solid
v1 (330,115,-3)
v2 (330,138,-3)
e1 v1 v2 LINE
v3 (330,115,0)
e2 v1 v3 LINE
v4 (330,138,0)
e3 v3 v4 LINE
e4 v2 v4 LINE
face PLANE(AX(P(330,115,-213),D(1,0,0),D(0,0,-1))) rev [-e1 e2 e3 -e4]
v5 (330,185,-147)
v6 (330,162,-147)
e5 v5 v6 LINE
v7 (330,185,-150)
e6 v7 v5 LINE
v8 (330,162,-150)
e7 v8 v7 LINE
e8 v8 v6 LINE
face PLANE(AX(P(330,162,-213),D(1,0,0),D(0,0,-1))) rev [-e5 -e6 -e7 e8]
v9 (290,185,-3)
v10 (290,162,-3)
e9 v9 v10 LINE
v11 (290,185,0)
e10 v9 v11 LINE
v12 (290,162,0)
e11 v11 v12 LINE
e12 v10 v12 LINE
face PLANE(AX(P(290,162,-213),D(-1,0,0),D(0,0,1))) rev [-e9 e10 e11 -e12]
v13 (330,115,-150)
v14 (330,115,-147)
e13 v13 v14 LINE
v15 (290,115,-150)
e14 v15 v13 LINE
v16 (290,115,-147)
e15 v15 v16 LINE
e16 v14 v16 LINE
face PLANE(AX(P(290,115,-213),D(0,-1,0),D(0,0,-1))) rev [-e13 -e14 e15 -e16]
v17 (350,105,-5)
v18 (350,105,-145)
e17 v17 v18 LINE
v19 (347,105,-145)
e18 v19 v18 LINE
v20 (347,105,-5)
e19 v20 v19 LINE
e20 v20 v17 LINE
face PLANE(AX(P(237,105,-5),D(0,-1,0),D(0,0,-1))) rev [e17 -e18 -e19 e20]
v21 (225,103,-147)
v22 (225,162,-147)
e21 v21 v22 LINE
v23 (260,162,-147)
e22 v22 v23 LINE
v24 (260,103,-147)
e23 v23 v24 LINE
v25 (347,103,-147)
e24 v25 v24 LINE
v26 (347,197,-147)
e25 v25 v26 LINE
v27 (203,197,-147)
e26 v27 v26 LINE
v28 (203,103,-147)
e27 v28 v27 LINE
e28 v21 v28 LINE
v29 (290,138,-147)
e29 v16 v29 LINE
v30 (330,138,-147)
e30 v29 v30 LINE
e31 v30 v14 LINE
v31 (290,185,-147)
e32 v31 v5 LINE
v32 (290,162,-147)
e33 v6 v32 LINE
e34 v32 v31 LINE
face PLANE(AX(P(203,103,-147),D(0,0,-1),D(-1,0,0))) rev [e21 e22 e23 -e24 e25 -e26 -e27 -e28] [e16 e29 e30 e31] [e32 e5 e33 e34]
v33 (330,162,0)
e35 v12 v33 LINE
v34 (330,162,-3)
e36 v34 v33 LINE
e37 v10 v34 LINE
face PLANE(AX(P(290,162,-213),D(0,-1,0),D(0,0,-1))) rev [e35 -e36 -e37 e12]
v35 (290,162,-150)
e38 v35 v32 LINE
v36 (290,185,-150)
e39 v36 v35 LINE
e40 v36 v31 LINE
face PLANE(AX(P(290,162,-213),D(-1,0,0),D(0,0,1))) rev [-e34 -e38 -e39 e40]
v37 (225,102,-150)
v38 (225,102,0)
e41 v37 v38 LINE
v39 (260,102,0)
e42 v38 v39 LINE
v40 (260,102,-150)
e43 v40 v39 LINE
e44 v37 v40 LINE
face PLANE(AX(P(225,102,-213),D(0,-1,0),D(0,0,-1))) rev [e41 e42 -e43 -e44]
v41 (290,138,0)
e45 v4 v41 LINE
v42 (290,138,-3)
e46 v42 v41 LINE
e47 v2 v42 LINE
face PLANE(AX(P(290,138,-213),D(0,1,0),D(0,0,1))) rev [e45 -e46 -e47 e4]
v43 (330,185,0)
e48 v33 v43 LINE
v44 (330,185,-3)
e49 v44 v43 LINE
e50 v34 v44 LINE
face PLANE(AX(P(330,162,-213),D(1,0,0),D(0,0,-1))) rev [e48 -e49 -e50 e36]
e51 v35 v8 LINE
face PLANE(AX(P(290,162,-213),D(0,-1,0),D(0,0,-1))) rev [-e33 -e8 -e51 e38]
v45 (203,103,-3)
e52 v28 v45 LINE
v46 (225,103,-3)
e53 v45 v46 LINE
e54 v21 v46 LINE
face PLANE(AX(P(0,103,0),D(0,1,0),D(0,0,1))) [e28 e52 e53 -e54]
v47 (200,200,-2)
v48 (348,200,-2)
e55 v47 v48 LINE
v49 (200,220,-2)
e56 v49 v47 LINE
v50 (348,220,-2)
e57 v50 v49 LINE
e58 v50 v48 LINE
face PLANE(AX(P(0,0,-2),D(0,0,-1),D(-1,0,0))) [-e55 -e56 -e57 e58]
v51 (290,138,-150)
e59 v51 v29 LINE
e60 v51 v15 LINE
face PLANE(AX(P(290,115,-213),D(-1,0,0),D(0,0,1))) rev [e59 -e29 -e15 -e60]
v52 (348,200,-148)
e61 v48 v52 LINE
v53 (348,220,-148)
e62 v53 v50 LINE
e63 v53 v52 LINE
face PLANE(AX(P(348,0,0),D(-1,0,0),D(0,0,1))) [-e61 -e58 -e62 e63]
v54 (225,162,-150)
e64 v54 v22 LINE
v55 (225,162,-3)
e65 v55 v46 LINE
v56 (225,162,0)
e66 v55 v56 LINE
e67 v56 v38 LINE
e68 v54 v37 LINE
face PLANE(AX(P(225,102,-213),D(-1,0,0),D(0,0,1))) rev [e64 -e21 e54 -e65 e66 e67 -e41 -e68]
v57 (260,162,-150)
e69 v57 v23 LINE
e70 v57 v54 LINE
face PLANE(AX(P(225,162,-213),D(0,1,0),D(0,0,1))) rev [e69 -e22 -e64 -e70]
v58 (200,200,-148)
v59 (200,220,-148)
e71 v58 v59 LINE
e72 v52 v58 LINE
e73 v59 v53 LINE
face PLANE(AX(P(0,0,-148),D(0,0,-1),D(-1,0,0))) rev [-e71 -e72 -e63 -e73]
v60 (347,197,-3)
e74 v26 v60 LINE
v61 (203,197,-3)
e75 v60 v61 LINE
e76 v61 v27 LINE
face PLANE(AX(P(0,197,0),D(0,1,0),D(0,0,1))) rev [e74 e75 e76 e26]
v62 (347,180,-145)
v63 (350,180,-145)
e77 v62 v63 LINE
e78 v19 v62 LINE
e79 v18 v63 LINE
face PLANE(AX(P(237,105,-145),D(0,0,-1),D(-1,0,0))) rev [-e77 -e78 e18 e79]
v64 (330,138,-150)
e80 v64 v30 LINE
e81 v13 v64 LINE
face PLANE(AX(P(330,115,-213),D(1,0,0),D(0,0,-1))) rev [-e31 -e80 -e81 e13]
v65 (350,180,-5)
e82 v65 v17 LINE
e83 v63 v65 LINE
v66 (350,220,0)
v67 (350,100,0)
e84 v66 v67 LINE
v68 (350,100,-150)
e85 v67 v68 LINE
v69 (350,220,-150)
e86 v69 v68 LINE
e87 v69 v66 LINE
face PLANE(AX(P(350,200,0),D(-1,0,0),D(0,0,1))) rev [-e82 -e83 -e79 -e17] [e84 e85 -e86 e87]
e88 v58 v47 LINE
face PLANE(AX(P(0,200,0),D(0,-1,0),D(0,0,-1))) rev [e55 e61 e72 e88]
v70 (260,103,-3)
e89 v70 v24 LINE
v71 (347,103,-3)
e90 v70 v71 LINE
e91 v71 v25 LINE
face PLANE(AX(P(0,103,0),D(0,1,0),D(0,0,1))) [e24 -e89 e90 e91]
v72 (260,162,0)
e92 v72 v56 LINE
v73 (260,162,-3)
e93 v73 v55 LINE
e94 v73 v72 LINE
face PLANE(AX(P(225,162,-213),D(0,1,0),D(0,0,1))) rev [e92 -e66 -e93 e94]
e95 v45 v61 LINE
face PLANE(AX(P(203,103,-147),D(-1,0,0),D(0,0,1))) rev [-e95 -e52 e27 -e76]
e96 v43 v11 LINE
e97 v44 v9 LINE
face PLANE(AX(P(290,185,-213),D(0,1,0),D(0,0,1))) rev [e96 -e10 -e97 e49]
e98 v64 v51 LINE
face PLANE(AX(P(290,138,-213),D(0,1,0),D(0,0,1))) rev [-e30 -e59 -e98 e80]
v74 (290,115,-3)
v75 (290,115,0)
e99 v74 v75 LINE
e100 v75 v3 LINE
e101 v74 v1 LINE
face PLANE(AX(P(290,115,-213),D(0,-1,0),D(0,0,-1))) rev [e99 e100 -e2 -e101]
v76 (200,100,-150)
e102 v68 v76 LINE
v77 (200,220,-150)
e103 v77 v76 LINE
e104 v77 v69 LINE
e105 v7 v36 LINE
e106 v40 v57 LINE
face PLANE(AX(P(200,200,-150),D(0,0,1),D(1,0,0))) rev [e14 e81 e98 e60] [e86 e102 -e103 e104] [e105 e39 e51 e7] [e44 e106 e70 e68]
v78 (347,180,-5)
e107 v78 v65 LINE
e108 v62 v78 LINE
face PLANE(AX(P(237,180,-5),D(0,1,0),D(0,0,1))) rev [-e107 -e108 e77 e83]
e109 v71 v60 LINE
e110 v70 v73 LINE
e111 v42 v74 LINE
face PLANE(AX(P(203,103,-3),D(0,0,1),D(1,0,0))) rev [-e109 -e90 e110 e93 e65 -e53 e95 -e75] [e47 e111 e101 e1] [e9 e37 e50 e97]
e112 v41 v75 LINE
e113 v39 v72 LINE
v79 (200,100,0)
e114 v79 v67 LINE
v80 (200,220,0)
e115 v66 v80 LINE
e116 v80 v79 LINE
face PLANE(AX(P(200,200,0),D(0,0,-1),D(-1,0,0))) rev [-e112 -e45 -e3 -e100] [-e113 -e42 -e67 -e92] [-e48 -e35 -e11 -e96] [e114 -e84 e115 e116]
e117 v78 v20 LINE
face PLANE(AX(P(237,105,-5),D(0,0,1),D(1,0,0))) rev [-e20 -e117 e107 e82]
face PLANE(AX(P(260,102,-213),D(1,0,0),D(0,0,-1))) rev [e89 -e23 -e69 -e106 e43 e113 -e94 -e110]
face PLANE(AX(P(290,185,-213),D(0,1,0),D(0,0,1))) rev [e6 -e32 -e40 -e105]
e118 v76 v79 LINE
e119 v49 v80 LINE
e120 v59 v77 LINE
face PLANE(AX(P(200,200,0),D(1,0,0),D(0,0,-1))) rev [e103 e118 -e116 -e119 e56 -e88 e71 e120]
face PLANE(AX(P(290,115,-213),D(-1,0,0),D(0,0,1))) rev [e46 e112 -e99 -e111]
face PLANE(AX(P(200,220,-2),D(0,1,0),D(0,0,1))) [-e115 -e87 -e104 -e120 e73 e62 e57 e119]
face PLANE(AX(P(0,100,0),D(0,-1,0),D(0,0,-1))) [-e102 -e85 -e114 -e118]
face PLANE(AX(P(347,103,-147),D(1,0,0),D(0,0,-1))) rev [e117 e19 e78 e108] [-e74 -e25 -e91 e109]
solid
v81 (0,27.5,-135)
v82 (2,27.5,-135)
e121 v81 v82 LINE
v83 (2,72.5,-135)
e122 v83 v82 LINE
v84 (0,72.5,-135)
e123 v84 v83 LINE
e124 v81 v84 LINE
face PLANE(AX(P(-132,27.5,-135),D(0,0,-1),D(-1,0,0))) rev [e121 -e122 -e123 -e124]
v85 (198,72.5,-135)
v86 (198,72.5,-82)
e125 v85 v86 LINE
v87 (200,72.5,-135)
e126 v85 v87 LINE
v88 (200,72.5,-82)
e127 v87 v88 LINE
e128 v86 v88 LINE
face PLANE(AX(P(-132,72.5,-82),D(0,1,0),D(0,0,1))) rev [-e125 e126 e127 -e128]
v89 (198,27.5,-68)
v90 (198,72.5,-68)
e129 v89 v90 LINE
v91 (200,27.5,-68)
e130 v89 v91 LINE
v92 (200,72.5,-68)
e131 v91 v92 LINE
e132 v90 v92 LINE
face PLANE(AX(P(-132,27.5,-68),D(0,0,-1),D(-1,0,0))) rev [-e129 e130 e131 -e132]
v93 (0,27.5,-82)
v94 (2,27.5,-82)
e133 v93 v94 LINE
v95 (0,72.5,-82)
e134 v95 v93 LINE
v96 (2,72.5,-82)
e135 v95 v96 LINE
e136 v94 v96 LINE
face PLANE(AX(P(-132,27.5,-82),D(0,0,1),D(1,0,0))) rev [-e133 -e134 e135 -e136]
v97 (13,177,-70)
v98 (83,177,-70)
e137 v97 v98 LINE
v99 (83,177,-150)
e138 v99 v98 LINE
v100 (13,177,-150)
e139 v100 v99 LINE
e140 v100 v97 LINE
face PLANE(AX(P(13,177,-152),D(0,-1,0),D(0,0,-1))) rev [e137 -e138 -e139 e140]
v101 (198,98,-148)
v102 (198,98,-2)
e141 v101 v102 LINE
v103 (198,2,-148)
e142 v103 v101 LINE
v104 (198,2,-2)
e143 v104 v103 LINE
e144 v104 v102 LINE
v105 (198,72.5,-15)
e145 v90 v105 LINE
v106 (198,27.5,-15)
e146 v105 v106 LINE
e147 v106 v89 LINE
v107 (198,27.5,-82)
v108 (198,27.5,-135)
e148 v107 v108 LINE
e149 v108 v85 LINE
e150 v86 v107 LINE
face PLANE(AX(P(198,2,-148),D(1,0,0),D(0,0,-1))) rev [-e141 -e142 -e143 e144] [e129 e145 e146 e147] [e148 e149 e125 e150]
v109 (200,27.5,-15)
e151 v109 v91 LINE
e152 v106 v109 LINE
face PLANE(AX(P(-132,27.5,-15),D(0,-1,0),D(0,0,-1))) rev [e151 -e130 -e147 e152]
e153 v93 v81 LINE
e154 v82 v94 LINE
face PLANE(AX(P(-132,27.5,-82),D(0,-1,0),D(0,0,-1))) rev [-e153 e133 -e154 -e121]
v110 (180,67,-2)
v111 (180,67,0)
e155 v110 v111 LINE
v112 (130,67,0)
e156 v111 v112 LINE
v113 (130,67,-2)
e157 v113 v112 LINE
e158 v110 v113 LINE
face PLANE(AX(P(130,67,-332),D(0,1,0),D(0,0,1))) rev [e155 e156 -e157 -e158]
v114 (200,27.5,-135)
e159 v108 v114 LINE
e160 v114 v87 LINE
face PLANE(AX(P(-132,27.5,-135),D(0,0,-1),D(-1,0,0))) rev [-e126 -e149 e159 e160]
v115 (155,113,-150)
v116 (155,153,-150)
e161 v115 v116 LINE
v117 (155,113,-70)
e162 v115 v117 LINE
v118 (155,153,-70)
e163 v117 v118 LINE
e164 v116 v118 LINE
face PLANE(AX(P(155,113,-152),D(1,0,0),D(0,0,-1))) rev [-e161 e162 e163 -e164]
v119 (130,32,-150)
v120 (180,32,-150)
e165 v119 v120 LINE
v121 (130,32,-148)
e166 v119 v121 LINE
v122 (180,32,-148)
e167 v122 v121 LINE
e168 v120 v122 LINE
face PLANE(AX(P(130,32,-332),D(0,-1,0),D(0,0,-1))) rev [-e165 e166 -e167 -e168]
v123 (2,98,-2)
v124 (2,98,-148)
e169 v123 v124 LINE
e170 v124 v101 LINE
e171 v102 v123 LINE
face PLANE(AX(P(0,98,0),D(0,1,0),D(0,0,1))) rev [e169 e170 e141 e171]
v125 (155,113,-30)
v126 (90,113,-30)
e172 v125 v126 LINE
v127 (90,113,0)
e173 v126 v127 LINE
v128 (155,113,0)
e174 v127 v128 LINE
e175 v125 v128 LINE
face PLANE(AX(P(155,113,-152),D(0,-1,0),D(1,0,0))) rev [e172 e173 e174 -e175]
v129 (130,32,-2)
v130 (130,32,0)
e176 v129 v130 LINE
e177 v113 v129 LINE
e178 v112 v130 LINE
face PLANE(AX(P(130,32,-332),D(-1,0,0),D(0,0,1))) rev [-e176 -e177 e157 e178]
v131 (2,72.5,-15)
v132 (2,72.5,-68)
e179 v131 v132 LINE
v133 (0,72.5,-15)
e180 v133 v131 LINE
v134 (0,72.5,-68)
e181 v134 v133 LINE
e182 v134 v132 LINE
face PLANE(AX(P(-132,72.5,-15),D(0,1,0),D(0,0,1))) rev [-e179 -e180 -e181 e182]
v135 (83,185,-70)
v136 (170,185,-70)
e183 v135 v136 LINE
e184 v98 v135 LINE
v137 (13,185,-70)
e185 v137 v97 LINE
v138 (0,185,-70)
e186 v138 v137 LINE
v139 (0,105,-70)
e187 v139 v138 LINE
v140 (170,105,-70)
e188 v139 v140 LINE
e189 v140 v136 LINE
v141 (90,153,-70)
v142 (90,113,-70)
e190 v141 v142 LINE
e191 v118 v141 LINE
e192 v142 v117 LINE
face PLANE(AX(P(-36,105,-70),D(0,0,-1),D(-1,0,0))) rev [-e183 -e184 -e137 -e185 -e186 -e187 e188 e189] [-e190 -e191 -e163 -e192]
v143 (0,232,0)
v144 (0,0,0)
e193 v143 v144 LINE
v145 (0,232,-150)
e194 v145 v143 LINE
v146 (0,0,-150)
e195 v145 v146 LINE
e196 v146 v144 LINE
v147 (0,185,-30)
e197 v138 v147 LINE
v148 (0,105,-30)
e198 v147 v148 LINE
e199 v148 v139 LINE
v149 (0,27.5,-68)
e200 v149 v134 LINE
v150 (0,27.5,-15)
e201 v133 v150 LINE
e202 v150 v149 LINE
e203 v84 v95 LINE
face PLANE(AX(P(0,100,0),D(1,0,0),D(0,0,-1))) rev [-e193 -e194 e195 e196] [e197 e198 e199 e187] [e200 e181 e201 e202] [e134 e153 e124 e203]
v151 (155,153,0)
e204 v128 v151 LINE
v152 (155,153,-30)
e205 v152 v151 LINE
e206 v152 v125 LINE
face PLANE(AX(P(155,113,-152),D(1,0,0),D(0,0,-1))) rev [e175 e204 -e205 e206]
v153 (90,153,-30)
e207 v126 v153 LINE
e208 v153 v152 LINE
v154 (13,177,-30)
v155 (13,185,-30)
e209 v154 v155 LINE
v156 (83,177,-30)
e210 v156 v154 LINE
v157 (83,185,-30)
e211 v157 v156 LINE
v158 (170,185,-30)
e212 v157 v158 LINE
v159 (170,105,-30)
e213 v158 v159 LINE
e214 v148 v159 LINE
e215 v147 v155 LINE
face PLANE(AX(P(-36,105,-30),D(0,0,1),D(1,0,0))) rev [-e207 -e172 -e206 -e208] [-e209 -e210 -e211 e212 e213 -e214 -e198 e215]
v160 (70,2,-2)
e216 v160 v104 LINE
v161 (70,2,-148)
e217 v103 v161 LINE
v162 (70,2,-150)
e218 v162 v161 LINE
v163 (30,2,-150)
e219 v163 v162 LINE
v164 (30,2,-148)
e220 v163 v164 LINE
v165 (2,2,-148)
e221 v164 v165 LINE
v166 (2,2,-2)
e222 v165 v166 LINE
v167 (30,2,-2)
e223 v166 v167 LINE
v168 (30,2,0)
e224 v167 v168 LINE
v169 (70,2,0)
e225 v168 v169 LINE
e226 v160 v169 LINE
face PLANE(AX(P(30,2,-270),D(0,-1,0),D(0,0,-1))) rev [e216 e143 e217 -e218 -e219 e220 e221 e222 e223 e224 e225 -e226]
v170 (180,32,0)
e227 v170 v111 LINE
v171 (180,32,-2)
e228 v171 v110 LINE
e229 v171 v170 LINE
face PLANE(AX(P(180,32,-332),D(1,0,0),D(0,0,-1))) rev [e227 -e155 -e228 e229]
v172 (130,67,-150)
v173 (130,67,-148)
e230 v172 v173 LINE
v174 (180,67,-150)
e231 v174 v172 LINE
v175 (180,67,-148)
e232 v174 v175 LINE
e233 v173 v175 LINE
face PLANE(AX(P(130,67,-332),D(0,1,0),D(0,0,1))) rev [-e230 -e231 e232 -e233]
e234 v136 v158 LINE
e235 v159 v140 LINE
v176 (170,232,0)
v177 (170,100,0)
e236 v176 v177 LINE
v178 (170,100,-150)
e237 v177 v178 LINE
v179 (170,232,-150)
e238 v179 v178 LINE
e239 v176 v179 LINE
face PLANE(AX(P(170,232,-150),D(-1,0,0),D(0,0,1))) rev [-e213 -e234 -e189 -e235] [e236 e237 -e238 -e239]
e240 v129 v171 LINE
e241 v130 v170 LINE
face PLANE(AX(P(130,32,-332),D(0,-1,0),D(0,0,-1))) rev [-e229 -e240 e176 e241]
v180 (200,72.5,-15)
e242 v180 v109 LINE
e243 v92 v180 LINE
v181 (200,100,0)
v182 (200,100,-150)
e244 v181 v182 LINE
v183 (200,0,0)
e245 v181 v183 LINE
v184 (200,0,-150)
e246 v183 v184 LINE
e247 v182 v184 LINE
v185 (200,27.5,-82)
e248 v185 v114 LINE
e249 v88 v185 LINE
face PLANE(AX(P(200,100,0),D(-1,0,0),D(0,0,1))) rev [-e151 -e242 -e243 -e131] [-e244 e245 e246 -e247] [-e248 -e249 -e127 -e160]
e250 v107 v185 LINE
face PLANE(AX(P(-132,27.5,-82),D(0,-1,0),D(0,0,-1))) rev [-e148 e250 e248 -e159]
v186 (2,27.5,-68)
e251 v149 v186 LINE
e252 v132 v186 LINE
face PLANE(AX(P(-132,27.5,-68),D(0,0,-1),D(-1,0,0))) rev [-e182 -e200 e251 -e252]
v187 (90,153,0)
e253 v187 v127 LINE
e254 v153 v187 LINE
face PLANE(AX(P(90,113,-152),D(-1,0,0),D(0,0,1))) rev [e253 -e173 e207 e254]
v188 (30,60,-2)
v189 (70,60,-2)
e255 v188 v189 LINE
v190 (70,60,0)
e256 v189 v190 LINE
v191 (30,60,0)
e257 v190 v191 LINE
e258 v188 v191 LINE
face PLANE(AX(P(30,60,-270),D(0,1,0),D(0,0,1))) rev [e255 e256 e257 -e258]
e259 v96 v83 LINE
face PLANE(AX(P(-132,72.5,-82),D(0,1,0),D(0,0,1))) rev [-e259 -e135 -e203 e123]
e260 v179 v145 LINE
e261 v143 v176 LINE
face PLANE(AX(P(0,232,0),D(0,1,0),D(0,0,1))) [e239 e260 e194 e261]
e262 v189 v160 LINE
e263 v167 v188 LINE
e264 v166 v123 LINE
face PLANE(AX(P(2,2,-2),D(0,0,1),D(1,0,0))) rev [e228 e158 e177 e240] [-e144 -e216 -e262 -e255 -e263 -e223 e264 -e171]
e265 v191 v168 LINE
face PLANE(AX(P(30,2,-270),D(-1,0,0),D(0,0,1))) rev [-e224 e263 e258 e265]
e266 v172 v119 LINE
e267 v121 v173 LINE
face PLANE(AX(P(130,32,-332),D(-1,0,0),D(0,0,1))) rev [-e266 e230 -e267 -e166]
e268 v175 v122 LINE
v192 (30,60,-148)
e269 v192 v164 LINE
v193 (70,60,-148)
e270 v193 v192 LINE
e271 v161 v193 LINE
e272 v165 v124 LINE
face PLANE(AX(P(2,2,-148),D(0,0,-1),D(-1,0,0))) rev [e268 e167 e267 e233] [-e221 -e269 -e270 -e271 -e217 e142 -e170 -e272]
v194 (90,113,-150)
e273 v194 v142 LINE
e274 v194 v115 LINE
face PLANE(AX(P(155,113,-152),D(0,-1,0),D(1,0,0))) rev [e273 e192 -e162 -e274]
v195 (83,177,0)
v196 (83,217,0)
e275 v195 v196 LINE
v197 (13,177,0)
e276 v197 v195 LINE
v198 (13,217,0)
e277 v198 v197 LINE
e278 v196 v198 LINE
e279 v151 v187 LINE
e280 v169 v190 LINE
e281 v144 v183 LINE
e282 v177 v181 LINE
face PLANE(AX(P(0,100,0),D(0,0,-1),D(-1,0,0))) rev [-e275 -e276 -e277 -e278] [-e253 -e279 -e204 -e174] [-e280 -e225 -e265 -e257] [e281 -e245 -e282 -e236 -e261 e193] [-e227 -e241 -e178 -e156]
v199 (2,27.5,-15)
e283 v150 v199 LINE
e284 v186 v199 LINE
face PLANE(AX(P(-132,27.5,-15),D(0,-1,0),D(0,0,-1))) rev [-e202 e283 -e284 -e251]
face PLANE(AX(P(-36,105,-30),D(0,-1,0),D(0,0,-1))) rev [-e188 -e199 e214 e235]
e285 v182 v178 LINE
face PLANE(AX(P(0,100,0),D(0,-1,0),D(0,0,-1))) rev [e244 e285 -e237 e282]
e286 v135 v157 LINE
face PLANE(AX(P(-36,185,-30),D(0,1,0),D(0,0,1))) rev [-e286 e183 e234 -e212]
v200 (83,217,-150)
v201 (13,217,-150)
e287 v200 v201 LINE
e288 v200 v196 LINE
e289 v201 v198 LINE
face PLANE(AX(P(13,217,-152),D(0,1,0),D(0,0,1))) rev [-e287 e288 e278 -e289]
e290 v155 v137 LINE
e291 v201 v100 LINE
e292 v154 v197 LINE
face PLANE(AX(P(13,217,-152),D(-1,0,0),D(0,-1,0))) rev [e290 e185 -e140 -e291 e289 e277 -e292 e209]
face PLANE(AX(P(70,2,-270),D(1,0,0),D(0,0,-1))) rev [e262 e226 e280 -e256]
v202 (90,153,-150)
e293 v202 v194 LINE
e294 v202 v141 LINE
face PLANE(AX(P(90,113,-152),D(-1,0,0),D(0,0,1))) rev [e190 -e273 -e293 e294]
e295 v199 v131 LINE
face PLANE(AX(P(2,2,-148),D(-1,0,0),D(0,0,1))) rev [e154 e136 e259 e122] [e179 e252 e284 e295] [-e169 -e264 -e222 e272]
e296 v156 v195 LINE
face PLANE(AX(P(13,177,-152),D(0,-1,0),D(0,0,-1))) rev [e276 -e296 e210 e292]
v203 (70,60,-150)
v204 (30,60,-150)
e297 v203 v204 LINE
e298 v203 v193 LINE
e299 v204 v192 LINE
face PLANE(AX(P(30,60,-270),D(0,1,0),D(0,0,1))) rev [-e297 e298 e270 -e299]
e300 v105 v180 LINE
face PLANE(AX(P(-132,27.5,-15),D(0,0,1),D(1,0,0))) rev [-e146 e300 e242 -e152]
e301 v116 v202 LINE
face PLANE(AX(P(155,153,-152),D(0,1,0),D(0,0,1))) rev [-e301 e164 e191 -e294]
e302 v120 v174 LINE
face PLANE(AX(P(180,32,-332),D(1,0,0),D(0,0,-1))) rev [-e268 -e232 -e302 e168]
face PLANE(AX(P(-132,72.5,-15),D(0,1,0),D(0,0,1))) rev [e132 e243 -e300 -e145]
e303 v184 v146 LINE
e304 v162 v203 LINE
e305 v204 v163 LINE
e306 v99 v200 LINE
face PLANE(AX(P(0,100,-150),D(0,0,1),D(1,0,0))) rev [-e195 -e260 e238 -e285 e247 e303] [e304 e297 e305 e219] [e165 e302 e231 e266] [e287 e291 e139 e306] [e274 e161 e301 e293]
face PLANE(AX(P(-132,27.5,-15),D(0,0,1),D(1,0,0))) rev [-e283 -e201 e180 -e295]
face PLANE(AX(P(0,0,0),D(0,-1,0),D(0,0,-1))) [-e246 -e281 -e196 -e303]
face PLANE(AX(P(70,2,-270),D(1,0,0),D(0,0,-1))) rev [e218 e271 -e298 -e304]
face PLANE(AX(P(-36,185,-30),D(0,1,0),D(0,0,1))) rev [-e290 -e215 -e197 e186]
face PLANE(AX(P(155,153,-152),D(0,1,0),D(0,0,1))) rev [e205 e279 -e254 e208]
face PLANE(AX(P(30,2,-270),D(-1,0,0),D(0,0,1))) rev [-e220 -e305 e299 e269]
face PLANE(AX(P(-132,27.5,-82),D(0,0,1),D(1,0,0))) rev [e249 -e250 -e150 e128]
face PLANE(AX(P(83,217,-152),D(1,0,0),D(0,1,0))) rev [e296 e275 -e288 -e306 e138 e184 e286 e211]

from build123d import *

# Parameters (mm, degrees)
BASE_BLOCK_SKETCH_W               = 200
BASE_BLOCK_SKETCH_H               = 150
BASE_BLOCK_DEPTH                  = 100
BASE_DOOR_OPENING_SKETCH_W        = 40
BASE_DOOR_OPENING_SKETCH_H        = 58
BASE_DOOR_OPENING_DEPTH           = 270
BASE_HOLLOW_SKETCH_W              = 196
BASE_HOLLOW_SKETCH_H              = 146
BASE_HOLLOW_2MM_WALL_DEPTH        = 98
BASE_FLOOR_SLAB_SKETCH_W          = 200
BASE_FLOOR_SLAB_SKETCH_H          = 150
BASE_FLOOR_SLAB_DEPTH             = 2
BASE_WINDOW_SKETCH_W              = 50
BASE_WINDOW_SKETCH_H              = 35
BASE_WINDOW_DEPTH                 = 332
BASE_SIDE_WINDOWS_SKETCH_W        = 53
BASE_SIDE_WINDOWS_SKETCH_H        = 45
BASE_SIDE_WINDOWS_DEPTH           = 332
SIDE_BLOCK_SKETCH_W               = 150
SIDE_BLOCK_SKETCH_H               = 150
SIDE_BLOCK_DEPTH                  = 100
SIDE_BLOCK_HOLLOW_SKETCH_W        = 144
SIDE_BLOCK_HOLLOW_SKETCH_H        = 144
SIDE_BLOCK_HOLLOW_3MM_WALL_DEPTH  = 97
SIDE_BLOCK_FLOOR_SLAB_SKETCH_W    = 150
SIDE_BLOCK_FLOOR_SLAB_SKETCH_H    = 150
SIDE_BLOCK_FLOOR_SLAB_DEPTH       = 3
SIDE_BLOCK_DOOR_SKETCH_W          = 35
SIDE_BLOCK_DOOR_SKETCH_H          = 60
SIDE_BLOCK_DOOR_OPENING_DEPTH     = 213
SIDE_BLOCK_WINDOWS_SKETCH_W       = 40
SIDE_BLOCK_WINDOWS_SKETCH_H       = 23
SIDE_BLOCK_WINDOWS_DEPTH          = 213
SIDE_BLOCK_FRONT_OPENING_SKETCH_W = 140
SIDE_BLOCK_FRONT_OPENING_SKETCH_H = 75
SIDE_BLOCK_FRONT_OPENING_DEPTH    = 113
PARAPET_FRONT_SKETCH_W            = 150
PARAPET_FRONT_SKETCH_H            = 20
PARAPET_FRONT_DEPTH               = 2
PARAPET_SIDE_SKETCH_W             = 147
PARAPET_SIDE_SKETCH_H             = 20
PARAPET_SIDE_DEPTH                = 2
PARAPET_BACK_SKETCH_W             = 150
PARAPET_BACK_SKETCH_H             = 20
PARAPET_BACK_DEPTH                = 2
TOWER_SKETCH_W                    = 170
TOWER_SKETCH_H                    = 150
TOWER_EXTENSION_DEPTH             = 132
TOWER_WINDOWS_SKETCH_W            = 65
TOWER_WINDOWS_SKETCH_H            = 40
TOWER_WINDOWS_SKETCH_W_2          = 70
TOWER_WINDOWS_DEPTH               = 152
TOWER_WINDOW_OPENING_SKETCH_W     = 40
TOWER_WINDOW_OPENING_SKETCH_H     = 80
TOWER_WINDOW_OPENING_DEPTH        = 206


with BuildPart() as part:
    # Base Block Sketch → Base Block (new body)
    with BuildSketch(Plane(origin=(0, 0, 0), x_dir=(1, 0, 0), z_dir=(0, 1, 0))):
        with Locations((100, 75)):
            Rectangle(BASE_BLOCK_SKETCH_W, BASE_BLOCK_SKETCH_H)
    extrude(amount=BASE_BLOCK_DEPTH)

    # Base Door Opening Sketch → Base Door Opening (cut)
    with BuildSketch(Plane.XY):
        with Locations((50, 31)):
            Rectangle(BASE_DOOR_OPENING_SKETCH_W, BASE_DOOR_OPENING_SKETCH_H)
    extrude(amount=-BASE_DOOR_OPENING_DEPTH, mode=Mode.SUBTRACT)

    # Base Hollow Sketch → Base Hollow 2mm Wall (cut)
    with BuildSketch(Plane(origin=(0, 100, 0), x_dir=(1, 0, 0), z_dir=(0, 1, 0))):
        with Locations((100, 75)):
            Rectangle(BASE_HOLLOW_SKETCH_W, BASE_HOLLOW_SKETCH_H)
    extrude(amount=-BASE_HOLLOW_2MM_WALL_DEPTH, mode=Mode.SUBTRACT)

    # Base Floor Slab Sketch → Base Floor Slab (add)
    with BuildSketch(Plane(origin=(0, 100, 0), x_dir=(1, 0, 0), z_dir=(0, 1, 0))):
        with Locations((100, 75)):
            Rectangle(BASE_FLOOR_SLAB_SKETCH_W, BASE_FLOOR_SLAB_SKETCH_H)
    extrude(amount=-BASE_FLOOR_SLAB_DEPTH)

    # Base Window Sketch → Base Window (cut)
    with BuildSketch(Plane.XY):
        with Locations((155, 49.5)):
            Rectangle(BASE_WINDOW_SKETCH_W, BASE_WINDOW_SKETCH_H)
    extrude(amount=-BASE_WINDOW_DEPTH, mode=Mode.SUBTRACT)

    # Base Side Windows Sketch → Base Side Windows (cut)
    with BuildSketch(Plane(origin=(200, 0, 0), x_dir=(0, 0, -1), z_dir=(1, 0, 0))):
        with Locations((41.5, 50)):
            Rectangle(BASE_SIDE_WINDOWS_SKETCH_W, BASE_SIDE_WINDOWS_SKETCH_H)
        with Locations((108.5, 50)):
            Rectangle(BASE_SIDE_WINDOWS_SKETCH_W, BASE_SIDE_WINDOWS_SKETCH_H)
    extrude(amount=-BASE_SIDE_WINDOWS_DEPTH, mode=Mode.SUBTRACT)

    # Tower Sketch → Tower Extension (add)
    with BuildSketch(Plane(origin=(0, 100, 0), x_dir=(1, 0, 0), z_dir=(0, 1, 0))):
        with Locations((85, 75)):
            Rectangle(TOWER_SKETCH_W, TOWER_SKETCH_H)
    extrude(amount=TOWER_EXTENSION_DEPTH)

    # Tower Windows Sketch → Tower Windows (cut)
    with BuildSketch(Plane.XY):
        with Locations((122.5, 133)):
            Rectangle(TOWER_WINDOWS_SKETCH_W, TOWER_WINDOWS_SKETCH_H)
        with Locations((48, 197)):
            Rectangle(TOWER_WINDOWS_SKETCH_W_2, TOWER_WINDOWS_SKETCH_H)
    extrude(amount=-TOWER_WINDOWS_DEPTH, mode=Mode.SUBTRACT)

    # Tower Window Opening Sketch → Tower Window Opening (cut)
    with BuildSketch(Plane(origin=(170, 0, 0), x_dir=(0, 0, -1), z_dir=(1, 0, 0))):
        with Locations((50, 145)):
            Rectangle(TOWER_WINDOW_OPENING_SKETCH_W, TOWER_WINDOW_OPENING_SKETCH_H)
    extrude(amount=-TOWER_WINDOW_OPENING_DEPTH, mode=Mode.SUBTRACT)


with BuildPart() as body_2:
    # Side Block Sketch → Side Block (new body)
    with BuildSketch(Plane(origin=(0, 100, 0), x_dir=(1, 0, 0), z_dir=(0, 1, 0))):
        with Locations((275, 75)):
            Rectangle(SIDE_BLOCK_SKETCH_W, SIDE_BLOCK_SKETCH_H)
    extrude(amount=SIDE_BLOCK_DEPTH)

    # Side Block Hollow Sketch → Side Block Hollow 3mm Wall (cut)
    with BuildSketch(Plane(origin=(0, 200, 0), x_dir=(1, 0, 0), z_dir=(0, 1, 0))):
        with Locations((275, 75)):
            Rectangle(SIDE_BLOCK_HOLLOW_SKETCH_W, SIDE_BLOCK_HOLLOW_SKETCH_H)
    extrude(amount=-SIDE_BLOCK_HOLLOW_3MM_WALL_DEPTH, mode=Mode.SUBTRACT)

    # Side Block Floor Slab Sketch → Side Block Floor Slab (add)
    with BuildSketch(Plane(origin=(0, 200, 0), x_dir=(1, 0, 0), z_dir=(0, 1, 0))):
        with Locations((275, 75)):
            Rectangle(SIDE_BLOCK_FLOOR_SLAB_SKETCH_W, SIDE_BLOCK_FLOOR_SLAB_SKETCH_H)
    extrude(amount=-SIDE_BLOCK_FLOOR_SLAB_DEPTH)

    # Side Block Door Sketch → Side Block Door Opening (cut)
    with BuildSketch(Plane.XY):
        with Locations((242.5, 132)):
            Rectangle(SIDE_BLOCK_DOOR_SKETCH_W, SIDE_BLOCK_DOOR_SKETCH_H)
    extrude(amount=-SIDE_BLOCK_DOOR_OPENING_DEPTH, mode=Mode.SUBTRACT)

    # Side Block Windows Sketch → Side Block Windows (cut)
    with BuildSketch(Plane.XY):
        with Locations((310, 126.5)):
            Rectangle(SIDE_BLOCK_WINDOWS_SKETCH_W, SIDE_BLOCK_WINDOWS_SKETCH_H)
        with Locations((310, 173.5)):
            Rectangle(SIDE_BLOCK_WINDOWS_SKETCH_W, SIDE_BLOCK_WINDOWS_SKETCH_H)
    extrude(amount=-SIDE_BLOCK_WINDOWS_DEPTH, mode=Mode.SUBTRACT)

    # Side Block Front Opening Sketch → Side Block Front Opening (cut)
    with BuildSketch(Plane(origin=(350, 0, 0), x_dir=(0, 0, -1), z_dir=(1, 0, 0))):
        with Locations((75, 142.5)):
            Rectangle(SIDE_BLOCK_FRONT_OPENING_SKETCH_W, SIDE_BLOCK_FRONT_OPENING_SKETCH_H)
    extrude(amount=-SIDE_BLOCK_FRONT_OPENING_DEPTH, mode=Mode.SUBTRACT)

    # Parapet Front Sketch → Parapet Front (add)
    with BuildSketch(Plane.XY):
        with Locations((275, 210)):
            Rectangle(PARAPET_FRONT_SKETCH_W, PARAPET_FRONT_SKETCH_H)
    extrude(amount=-PARAPET_FRONT_DEPTH)

    # Parapet Side Sketch → Parapet Side (add)
    with BuildSketch(Plane(origin=(350, 0, 0), x_dir=(0, 0, -1), z_dir=(1, 0, 0))):
        with Locations((75.5, 210)):
            Rectangle(PARAPET_SIDE_SKETCH_W, PARAPET_SIDE_SKETCH_H)
    extrude(amount=-PARAPET_SIDE_DEPTH)

    # Parapet Back Sketch → Parapet Back (add)
    with BuildSketch(Plane(origin=(0, 0, -150), x_dir=(-1, 0, 0), z_dir=(0, 0, -1))):
        with Locations((-275, 210)):
            Rectangle(PARAPET_BACK_SKETCH_W, PARAPET_BACK_SKETCH_H)
    extrude(amount=-PARAPET_BACK_DEPTH)


solid = Compound([part.part, body_2.part])
